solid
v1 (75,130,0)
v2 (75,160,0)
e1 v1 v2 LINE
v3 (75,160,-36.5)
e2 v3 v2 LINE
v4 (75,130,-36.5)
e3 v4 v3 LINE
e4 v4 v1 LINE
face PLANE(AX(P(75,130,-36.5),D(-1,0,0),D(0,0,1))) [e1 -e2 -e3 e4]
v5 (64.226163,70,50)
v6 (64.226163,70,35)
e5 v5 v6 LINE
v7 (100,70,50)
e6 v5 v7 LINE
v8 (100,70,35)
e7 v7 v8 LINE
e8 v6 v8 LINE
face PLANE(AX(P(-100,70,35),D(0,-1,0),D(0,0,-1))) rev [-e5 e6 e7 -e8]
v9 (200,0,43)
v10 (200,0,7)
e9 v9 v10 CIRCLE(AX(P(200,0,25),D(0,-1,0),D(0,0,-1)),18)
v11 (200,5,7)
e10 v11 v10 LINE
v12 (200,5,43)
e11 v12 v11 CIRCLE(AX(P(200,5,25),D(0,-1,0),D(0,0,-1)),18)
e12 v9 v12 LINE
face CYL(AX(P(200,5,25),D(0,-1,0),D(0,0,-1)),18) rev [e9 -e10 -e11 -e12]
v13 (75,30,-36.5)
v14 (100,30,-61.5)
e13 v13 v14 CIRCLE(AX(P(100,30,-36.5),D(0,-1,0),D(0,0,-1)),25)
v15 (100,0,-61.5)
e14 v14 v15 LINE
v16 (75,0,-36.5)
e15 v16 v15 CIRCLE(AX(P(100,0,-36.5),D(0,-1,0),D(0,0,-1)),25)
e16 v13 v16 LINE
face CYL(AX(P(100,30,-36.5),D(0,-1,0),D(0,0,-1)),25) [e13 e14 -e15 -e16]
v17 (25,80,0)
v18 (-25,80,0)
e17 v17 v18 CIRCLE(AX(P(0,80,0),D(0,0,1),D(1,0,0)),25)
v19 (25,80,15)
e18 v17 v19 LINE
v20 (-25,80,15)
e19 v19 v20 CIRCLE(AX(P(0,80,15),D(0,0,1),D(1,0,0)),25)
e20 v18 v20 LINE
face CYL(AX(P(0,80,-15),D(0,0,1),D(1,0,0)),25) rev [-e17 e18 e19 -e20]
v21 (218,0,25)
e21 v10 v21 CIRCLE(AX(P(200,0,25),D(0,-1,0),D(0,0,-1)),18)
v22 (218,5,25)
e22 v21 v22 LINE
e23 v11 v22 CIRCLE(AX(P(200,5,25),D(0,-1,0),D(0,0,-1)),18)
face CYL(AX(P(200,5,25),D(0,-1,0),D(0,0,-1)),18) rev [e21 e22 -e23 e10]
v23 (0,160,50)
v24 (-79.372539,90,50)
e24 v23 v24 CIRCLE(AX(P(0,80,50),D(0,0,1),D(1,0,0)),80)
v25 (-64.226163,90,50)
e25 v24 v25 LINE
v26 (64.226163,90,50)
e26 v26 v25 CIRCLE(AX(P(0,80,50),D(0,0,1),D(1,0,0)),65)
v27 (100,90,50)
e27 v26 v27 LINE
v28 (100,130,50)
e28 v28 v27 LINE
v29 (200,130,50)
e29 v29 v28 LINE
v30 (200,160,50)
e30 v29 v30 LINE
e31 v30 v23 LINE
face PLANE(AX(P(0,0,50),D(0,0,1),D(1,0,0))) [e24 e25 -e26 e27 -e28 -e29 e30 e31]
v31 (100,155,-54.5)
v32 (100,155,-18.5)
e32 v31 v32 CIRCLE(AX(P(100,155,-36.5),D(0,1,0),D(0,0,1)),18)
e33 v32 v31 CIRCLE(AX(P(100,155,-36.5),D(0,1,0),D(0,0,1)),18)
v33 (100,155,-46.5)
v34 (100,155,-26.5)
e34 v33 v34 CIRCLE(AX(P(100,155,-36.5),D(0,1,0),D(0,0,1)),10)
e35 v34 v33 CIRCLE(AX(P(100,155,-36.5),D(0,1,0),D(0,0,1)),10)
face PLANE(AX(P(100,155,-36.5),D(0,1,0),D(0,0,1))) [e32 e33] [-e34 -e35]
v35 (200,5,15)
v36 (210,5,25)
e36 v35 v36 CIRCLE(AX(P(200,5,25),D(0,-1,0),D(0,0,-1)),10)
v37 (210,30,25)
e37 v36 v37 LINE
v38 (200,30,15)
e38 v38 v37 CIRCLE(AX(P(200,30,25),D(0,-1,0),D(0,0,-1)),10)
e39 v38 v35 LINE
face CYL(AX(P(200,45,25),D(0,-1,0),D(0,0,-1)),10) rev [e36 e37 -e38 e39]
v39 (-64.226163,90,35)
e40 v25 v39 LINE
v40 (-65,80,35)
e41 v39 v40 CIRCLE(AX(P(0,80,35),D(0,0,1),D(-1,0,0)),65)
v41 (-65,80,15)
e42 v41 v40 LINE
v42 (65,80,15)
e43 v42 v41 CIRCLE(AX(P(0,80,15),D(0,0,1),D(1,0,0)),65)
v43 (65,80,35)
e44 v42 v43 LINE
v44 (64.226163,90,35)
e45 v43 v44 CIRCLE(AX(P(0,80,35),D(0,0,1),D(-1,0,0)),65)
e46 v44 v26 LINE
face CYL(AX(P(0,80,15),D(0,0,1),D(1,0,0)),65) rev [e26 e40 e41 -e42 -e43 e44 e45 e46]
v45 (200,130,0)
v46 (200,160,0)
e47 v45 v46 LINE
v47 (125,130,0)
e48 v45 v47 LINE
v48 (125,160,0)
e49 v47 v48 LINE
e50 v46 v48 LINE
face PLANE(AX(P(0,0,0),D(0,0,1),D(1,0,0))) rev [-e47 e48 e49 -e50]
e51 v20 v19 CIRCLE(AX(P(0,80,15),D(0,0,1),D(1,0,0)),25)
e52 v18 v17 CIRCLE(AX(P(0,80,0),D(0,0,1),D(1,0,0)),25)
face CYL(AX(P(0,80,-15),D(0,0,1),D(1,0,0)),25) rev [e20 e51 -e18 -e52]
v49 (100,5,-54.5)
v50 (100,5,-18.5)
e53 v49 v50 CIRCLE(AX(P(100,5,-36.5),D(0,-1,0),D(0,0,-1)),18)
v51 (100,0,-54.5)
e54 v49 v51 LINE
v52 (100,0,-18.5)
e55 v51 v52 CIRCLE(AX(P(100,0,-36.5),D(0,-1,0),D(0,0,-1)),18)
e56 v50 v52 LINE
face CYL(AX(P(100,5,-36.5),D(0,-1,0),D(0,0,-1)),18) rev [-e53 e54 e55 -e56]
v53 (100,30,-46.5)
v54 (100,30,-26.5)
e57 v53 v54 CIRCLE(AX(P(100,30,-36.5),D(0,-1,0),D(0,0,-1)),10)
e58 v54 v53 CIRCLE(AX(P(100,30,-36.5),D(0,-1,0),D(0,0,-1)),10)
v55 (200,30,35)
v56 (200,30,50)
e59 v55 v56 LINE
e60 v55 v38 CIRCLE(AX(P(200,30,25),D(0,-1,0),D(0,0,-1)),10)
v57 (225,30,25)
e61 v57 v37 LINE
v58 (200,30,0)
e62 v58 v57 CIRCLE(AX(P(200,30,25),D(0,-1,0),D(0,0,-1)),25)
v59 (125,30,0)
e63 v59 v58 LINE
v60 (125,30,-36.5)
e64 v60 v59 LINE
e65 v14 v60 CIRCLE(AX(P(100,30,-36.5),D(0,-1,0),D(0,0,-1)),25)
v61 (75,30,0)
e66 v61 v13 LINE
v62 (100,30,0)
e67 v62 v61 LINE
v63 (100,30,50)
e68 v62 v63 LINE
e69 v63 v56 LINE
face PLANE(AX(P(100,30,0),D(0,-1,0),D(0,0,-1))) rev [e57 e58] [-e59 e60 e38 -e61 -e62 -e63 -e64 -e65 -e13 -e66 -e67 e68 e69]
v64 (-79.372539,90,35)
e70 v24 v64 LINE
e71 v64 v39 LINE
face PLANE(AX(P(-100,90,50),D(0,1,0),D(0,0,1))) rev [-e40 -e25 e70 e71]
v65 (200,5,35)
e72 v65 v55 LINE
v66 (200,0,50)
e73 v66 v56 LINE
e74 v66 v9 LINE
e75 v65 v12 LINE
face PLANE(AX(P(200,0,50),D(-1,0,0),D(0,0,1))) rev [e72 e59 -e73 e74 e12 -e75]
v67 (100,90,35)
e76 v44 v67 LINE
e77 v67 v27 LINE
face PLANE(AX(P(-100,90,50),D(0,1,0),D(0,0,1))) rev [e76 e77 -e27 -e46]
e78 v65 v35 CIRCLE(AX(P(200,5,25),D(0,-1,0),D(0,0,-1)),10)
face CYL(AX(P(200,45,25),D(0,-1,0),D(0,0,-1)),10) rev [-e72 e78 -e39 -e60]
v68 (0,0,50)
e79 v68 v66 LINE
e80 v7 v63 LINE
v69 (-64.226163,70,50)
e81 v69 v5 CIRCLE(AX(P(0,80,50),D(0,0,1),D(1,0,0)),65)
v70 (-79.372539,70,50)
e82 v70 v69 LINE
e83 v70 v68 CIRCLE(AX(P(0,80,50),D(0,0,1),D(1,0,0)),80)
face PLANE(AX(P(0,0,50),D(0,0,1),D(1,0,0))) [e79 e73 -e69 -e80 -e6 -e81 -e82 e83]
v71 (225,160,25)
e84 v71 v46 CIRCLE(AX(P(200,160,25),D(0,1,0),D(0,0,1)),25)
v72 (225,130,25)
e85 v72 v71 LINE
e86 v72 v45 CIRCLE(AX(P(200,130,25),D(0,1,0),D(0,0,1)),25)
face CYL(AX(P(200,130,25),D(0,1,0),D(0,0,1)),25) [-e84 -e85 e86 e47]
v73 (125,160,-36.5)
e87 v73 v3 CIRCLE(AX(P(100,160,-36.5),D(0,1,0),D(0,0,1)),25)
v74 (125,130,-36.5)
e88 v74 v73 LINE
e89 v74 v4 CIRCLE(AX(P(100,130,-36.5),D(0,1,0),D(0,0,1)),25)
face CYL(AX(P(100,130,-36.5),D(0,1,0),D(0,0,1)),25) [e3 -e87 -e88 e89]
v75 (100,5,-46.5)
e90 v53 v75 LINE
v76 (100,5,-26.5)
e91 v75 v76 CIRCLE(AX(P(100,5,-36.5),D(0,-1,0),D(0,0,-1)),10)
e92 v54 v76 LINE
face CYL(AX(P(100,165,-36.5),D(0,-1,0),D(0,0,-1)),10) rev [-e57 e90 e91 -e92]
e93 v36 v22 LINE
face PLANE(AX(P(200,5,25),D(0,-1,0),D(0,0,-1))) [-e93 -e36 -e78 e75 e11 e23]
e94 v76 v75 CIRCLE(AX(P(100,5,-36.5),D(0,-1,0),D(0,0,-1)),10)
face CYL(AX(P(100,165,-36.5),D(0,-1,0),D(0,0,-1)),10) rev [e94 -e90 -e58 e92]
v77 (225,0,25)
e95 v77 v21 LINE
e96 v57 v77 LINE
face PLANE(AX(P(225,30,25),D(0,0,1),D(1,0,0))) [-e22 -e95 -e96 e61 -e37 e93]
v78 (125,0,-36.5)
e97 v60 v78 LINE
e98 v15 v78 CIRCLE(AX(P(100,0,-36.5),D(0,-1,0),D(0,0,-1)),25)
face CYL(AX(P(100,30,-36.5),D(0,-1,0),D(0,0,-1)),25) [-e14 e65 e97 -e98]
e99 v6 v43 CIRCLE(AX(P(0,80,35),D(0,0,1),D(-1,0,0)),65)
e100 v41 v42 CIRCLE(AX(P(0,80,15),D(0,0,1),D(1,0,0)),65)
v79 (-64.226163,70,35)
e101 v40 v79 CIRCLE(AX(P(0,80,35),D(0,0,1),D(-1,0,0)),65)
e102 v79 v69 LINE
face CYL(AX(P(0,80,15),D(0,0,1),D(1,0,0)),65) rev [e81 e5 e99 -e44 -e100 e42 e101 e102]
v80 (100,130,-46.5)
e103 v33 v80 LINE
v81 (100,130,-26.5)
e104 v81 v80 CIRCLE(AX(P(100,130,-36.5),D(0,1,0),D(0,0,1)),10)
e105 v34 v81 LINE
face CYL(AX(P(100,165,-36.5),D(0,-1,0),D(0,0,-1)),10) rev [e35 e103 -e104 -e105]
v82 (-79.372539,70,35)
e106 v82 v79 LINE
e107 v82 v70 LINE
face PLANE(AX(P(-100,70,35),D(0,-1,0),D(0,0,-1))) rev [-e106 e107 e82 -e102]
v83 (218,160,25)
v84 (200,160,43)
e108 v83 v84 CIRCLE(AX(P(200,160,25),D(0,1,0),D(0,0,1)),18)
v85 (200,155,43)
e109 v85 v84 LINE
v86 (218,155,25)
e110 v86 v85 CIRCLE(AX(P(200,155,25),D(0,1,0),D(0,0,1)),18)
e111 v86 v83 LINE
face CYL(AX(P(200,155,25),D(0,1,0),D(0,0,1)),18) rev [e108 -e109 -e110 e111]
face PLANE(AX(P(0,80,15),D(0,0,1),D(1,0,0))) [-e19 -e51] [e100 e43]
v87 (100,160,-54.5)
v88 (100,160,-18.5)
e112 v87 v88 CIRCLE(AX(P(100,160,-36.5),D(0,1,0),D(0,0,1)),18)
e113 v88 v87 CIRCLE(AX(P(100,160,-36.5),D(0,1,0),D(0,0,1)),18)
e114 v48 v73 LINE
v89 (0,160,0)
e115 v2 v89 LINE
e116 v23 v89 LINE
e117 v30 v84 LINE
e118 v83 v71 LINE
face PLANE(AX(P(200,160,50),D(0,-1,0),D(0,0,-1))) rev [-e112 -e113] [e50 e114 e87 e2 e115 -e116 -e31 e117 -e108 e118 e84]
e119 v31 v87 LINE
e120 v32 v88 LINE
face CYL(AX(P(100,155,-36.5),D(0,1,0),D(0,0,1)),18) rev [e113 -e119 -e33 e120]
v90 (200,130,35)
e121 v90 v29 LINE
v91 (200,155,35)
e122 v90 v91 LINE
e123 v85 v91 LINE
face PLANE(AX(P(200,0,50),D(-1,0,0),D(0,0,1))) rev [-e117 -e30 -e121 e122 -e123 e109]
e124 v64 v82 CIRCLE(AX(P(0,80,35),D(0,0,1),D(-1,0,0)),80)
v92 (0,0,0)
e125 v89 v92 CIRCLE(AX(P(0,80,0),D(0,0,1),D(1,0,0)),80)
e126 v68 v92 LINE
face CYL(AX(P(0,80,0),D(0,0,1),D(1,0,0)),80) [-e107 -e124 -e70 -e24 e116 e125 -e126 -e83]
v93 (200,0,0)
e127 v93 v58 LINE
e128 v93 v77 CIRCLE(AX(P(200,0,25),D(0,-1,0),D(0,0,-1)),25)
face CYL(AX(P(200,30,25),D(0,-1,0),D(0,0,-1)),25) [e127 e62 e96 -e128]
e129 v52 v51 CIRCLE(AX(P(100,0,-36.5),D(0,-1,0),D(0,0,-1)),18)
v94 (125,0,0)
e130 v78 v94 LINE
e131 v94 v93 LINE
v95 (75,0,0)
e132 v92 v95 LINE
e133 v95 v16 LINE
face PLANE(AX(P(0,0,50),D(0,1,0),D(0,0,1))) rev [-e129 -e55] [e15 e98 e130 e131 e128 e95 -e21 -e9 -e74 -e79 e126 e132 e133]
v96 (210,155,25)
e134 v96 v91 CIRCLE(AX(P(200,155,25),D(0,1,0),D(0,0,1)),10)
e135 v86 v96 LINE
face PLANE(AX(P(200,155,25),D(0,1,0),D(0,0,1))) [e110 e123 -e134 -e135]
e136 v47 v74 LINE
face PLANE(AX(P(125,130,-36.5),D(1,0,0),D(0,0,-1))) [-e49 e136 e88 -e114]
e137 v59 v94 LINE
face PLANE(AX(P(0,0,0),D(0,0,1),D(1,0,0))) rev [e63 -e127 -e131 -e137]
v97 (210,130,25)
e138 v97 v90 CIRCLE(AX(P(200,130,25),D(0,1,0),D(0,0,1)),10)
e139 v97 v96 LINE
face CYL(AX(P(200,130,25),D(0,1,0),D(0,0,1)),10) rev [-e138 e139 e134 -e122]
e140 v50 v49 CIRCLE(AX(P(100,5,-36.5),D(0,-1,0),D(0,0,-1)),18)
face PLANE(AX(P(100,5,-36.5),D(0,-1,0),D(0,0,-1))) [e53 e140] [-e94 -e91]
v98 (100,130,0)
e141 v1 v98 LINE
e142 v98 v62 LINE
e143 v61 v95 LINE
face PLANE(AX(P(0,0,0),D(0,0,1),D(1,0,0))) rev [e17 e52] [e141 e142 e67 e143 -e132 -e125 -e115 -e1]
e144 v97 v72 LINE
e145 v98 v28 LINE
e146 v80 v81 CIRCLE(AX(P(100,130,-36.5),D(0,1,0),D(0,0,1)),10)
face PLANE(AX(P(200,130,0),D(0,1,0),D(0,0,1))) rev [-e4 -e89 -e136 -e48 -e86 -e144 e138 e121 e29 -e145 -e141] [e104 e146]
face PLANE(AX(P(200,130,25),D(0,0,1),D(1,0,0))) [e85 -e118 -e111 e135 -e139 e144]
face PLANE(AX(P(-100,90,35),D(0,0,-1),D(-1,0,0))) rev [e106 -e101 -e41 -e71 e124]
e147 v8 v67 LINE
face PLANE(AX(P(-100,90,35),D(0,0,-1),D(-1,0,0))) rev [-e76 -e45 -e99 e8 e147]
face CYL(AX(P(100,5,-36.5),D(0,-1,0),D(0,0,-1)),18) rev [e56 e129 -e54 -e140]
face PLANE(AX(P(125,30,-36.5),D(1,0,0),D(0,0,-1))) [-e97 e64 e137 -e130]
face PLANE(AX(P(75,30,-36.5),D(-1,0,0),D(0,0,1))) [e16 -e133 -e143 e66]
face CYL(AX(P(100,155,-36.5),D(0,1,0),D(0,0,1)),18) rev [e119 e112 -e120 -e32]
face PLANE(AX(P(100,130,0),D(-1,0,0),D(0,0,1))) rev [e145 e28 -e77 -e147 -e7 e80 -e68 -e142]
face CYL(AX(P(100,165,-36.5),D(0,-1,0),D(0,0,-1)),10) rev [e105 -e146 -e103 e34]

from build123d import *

# Parameters (mm, degrees)
BASE_BLOCK_SKETCH_W              = 200
BASE_BLOCK_SKETCH_H              = 160
BASE_BLOCK_DEPTH                 = 50
BEARING_HOUSING_DEPTH            = 50
BASE_RELIEF_CUT_SKETCH_W         = 100
BASE_RELIEF_CUT_SKETCH_H         = 100
BASE_RELIEF_CUT_DEPTH            = 50
BEARING_BORE_SKETCH_R            = 65
BEARING_BORE_DEPTH_35_DEPTH      = 35
FORK_SLOT_DEPTH                  = 200
UPPER_ARM_DEPTH                  = 30
UPPER_START                      = -30
UPPER_ARM_LUG_DEPTH              = 30
UPPER_LUG_COUNTERBORE_SKETCH_R   = 18
UPPER_LUG_COUNTERBORE_36X5_DEPTH = 5
UPPER_LUG_HOLE_SKETCH_R          = 7
UPPER_LUG_HOLE_14_DEPTH          = 50
UPPER_START_2                    = -5
UPPER_ARM_COUNTERBORE_SKETCH_R   = 18
UPPER_ARM_COUNTERBORE_36X5_DEPTH = 5
UPPER_START_3                    = -50
UPPER_ARM_HOLE_SKETCH_R          = 7
UPPER_ARM_HOLE_14_DEPTH          = 50
LOWER_ARM_DEPTH                  = 30
LOWER_START                      = -30
LOWER_ARM_LUG_DEPTH              = 30
LOWER_ARM_COUNTERBORE_SKETCH_R   = 18
LOWER_ARM_COUNTERBORE_36X5_DEPTH = 5
LOWER_ARM_HOLE_SKETCH_R          = 10
LOWER_ARM_HOLE_20_DEPTH          = 40
CROSS_HOLE_SKETCH_R              = 10
CROSS_HOLE_20_DEPTH              = 160
LOWER_START_2                    = -5
LOWER_LUG_COUNTERBORE_SKETCH_R   = 18
LOWER_LUG_COUNTERBORE_36X5_DEPTH = 5
LOWER_LUG_HOLE_SKETCH_R          = 10
LOWER_LUG_HOLE_20_DEPTH          = 30
SHAFT_BORE_SKETCH_R              = 25
SHAFT_BORE_50_DEPTH              = 30


with BuildPart() as part:
    # Base Block Sketch → Base Block (new body)
    with BuildSketch(Plane.XY):
        with Locations((100, 80)):
            Rectangle(BASE_BLOCK_SKETCH_W, BASE_BLOCK_SKETCH_H)
    extrude(amount=BASE_BLOCK_DEPTH)

    # Bearing Housing Sketch → Bearing Housing (add)
    with BuildSketch(Plane.XY.offset(50)):
        with BuildLine():
            Line((0, 160), (0, 0))
            ThreePointArc((0, 0), (-80, 80), (0, 160))
        make_face()
    extrude(amount=-BEARING_HOUSING_DEPTH)

    # Base Relief Cut Sketch → Base Relief Cut (cut)
    with BuildSketch(Plane.XY.offset(50)):
        with Locations((150, 80)):
            Rectangle(BASE_RELIEF_CUT_SKETCH_W, BASE_RELIEF_CUT_SKETCH_H)
    extrude(amount=-BASE_RELIEF_CUT_DEPTH, mode=Mode.SUBTRACT)

    # Bearing Bore Sketch → Bearing Bore Depth 35 (cut)
    with BuildSketch(Plane.XY.offset(50)):
        with Locations((0, 80)):
            Circle(BEARING_BORE_SKETCH_R)
    extrude(amount=-BEARING_BORE_DEPTH_35_DEPTH, mode=Mode.SUBTRACT)

    # Fork Slot Sketch → Fork Slot (cut)
    with BuildSketch(Plane(origin=(100, 0, 0), x_dir=(0, 0, -1), z_dir=(1, 0, 0))):
        Polygon((-50, 80), (-50, 90), (-35, 90), (-35, 70), (-50, 70), align=None)
    extrude(amount=-FORK_SLOT_DEPTH, mode=Mode.SUBTRACT)

    # Upper Arm Sketch → Upper Arm (add)
    with BuildSketch(Plane.XZ):
        with BuildLine():
            Line((125, 0), (100, 0))
            Line((100, 0), (75, 0))
            Line((75, 0), (75, -36.5))
            ThreePointArc((75, -36.5), (100, -61.5), (125, -36.5))
            Line((125, -36.5), (125, 0))
        make_face()
    extrude(amount=-UPPER_ARM_DEPTH)

    # Upper Arm Lug Sketch → Upper Arm Lug (add)
    with BuildSketch(Plane(origin=(0, 160, 0), x_dir=(1, 0, 0), z_dir=(0, 1, 0)).offset(UPPER_START)):
        with BuildLine():
            Line((75, 36.5), (75, 0))
            Line((75, 0), (125, 0))
            Line((125, 0), (125, 36.5))
            ThreePointArc((125, 36.5), (100, 61.5), (75, 36.5))
        make_face()
    extrude(amount=UPPER_ARM_LUG_DEPTH)

    # Upper Lug Counterbore Sketch → Upper Lug Counterbore Ø36x5 (cut)
    with BuildSketch(Plane(origin=(0, 160, 0), x_dir=(1, 0, 0), z_dir=(0, 1, 0))):
        with Locations(Location((100, 36.5, 0), (0, 0, 270))):
            Circle(UPPER_LUG_COUNTERBORE_SKETCH_R)
    extrude(amount=-UPPER_LUG_COUNTERBORE_36X5_DEPTH, mode=Mode.SUBTRACT)

    # Upper Lug Hole Sketch → Upper Lug Hole Ø14 (cut)
    with BuildSketch(Plane(origin=(0, 155, 0), x_dir=(1, 0, 0), z_dir=(0, 1, 0))):
        with Locations(Location((100, 36.5, 0), (0, 0, 270))):
            Circle(UPPER_LUG_HOLE_SKETCH_R)
    extrude(amount=-UPPER_LUG_HOLE_14_DEPTH, mode=Mode.SUBTRACT)

    # Upper Arm Counterbore Sketch → Upper Arm Counterbore Ø36x5 (cut)
    with BuildSketch(Plane.XZ.offset(UPPER_START_2)):
        with Locations(Location((100, -36.5, 0), (0, 0, 90))):
            Circle(UPPER_ARM_COUNTERBORE_SKETCH_R)
    extrude(amount=UPPER_ARM_COUNTERBORE_36X5_DEPTH, mode=Mode.SUBTRACT)

    # Upper Arm Hole Sketch → Upper Arm Hole Ø14 (cut)
    with BuildSketch(Plane.XZ.offset(-5).offset(UPPER_START_3)):
        with Locations(Location((100, -36.5, 0), (0, 0, 90))):
            Circle(UPPER_ARM_HOLE_SKETCH_R)
    extrude(amount=UPPER_ARM_HOLE_14_DEPTH, mode=Mode.SUBTRACT)

    # Lower Arm Sketch → Lower Arm (add)
    with BuildSketch(Plane.XZ):
        with BuildLine():
            Line((225, 25), (200, 25))
            Line((200, 25), (200, 50))
            ThreePointArc((200, 50), (182.32233047, 7.32233047), (225, 25))
        make_face()
    extrude(amount=-LOWER_ARM_DEPTH)

    # Lower Arm Lug Sketch → Lower Arm Lug (add)
    with BuildSketch(Plane(origin=(0, 160, 0), x_dir=(1, 0, 0), z_dir=(0, 1, 0)).offset(LOWER_START)):
        with BuildLine():
            Line((200, -25), (225, -25))
            ThreePointArc((225, -25), (217.67766953, -7.32233047), (200, 0))
            Line((200, 0), (200, -25))
        make_face()
    extrude(amount=LOWER_ARM_LUG_DEPTH)

    # Lower Arm Counterbore Sketch → Lower Arm Counterbore Ø36x5 (cut)
    with BuildSketch(Plane.XZ):
        with Locations((200, 25)):
            Circle(LOWER_ARM_COUNTERBORE_SKETCH_R)
    extrude(amount=-LOWER_ARM_COUNTERBORE_36X5_DEPTH, mode=Mode.SUBTRACT)

    # Lower Arm Hole Sketch → Lower Arm Hole Ø20 (cut)
    with BuildSketch(Plane.XZ.offset(-5)):
        with Locations((200, 25)):
            Circle(LOWER_ARM_HOLE_SKETCH_R)
    extrude(amount=-LOWER_ARM_HOLE_20_DEPTH, mode=Mode.SUBTRACT)

    # Cross Hole Sketch → Cross Hole Ø20 (cut)
    with BuildSketch(Plane.XZ.offset(-5)):
        with Locations(Location((100, -36.5, 0), (0, 0, 270))):
            Circle(CROSS_HOLE_SKETCH_R)
    extrude(amount=-CROSS_HOLE_20_DEPTH, mode=Mode.SUBTRACT)

    # Lower Lug Counterbore Sketch → Lower Lug Counterbore Ø36x5 (cut)
    with BuildSketch(Plane(origin=(0, 160, 0), x_dir=(1, 0, 0), z_dir=(0, 1, 0)).offset(LOWER_START_2)):
        with Locations((200, -25)):
            Circle(LOWER_LUG_COUNTERBORE_SKETCH_R)
    extrude(amount=LOWER_LUG_COUNTERBORE_36X5_DEPTH, mode=Mode.SUBTRACT)

    # Lower Lug Hole Sketch → Lower Lug Hole Ø20 (cut)
    with BuildSketch(Plane(origin=(0, 160, 0), x_dir=(1, 0, 0), z_dir=(0, 1, 0)).offset(LOWER_START)):
        with Locations((200, -25)):
            Circle(LOWER_LUG_HOLE_SKETCH_R)
    extrude(amount=LOWER_LUG_HOLE_20_DEPTH, mode=Mode.SUBTRACT)

    # Shaft Bore Sketch → Shaft Bore Ø50 (cut)
    with BuildSketch(Plane.XY.offset(15)):
        with Locations((0, 80)):
            Circle(SHAFT_BORE_SKETCH_R)
    extrude(amount=-SHAFT_BORE_50_DEPTH, mode=Mode.SUBTRACT)


solid = part.part
